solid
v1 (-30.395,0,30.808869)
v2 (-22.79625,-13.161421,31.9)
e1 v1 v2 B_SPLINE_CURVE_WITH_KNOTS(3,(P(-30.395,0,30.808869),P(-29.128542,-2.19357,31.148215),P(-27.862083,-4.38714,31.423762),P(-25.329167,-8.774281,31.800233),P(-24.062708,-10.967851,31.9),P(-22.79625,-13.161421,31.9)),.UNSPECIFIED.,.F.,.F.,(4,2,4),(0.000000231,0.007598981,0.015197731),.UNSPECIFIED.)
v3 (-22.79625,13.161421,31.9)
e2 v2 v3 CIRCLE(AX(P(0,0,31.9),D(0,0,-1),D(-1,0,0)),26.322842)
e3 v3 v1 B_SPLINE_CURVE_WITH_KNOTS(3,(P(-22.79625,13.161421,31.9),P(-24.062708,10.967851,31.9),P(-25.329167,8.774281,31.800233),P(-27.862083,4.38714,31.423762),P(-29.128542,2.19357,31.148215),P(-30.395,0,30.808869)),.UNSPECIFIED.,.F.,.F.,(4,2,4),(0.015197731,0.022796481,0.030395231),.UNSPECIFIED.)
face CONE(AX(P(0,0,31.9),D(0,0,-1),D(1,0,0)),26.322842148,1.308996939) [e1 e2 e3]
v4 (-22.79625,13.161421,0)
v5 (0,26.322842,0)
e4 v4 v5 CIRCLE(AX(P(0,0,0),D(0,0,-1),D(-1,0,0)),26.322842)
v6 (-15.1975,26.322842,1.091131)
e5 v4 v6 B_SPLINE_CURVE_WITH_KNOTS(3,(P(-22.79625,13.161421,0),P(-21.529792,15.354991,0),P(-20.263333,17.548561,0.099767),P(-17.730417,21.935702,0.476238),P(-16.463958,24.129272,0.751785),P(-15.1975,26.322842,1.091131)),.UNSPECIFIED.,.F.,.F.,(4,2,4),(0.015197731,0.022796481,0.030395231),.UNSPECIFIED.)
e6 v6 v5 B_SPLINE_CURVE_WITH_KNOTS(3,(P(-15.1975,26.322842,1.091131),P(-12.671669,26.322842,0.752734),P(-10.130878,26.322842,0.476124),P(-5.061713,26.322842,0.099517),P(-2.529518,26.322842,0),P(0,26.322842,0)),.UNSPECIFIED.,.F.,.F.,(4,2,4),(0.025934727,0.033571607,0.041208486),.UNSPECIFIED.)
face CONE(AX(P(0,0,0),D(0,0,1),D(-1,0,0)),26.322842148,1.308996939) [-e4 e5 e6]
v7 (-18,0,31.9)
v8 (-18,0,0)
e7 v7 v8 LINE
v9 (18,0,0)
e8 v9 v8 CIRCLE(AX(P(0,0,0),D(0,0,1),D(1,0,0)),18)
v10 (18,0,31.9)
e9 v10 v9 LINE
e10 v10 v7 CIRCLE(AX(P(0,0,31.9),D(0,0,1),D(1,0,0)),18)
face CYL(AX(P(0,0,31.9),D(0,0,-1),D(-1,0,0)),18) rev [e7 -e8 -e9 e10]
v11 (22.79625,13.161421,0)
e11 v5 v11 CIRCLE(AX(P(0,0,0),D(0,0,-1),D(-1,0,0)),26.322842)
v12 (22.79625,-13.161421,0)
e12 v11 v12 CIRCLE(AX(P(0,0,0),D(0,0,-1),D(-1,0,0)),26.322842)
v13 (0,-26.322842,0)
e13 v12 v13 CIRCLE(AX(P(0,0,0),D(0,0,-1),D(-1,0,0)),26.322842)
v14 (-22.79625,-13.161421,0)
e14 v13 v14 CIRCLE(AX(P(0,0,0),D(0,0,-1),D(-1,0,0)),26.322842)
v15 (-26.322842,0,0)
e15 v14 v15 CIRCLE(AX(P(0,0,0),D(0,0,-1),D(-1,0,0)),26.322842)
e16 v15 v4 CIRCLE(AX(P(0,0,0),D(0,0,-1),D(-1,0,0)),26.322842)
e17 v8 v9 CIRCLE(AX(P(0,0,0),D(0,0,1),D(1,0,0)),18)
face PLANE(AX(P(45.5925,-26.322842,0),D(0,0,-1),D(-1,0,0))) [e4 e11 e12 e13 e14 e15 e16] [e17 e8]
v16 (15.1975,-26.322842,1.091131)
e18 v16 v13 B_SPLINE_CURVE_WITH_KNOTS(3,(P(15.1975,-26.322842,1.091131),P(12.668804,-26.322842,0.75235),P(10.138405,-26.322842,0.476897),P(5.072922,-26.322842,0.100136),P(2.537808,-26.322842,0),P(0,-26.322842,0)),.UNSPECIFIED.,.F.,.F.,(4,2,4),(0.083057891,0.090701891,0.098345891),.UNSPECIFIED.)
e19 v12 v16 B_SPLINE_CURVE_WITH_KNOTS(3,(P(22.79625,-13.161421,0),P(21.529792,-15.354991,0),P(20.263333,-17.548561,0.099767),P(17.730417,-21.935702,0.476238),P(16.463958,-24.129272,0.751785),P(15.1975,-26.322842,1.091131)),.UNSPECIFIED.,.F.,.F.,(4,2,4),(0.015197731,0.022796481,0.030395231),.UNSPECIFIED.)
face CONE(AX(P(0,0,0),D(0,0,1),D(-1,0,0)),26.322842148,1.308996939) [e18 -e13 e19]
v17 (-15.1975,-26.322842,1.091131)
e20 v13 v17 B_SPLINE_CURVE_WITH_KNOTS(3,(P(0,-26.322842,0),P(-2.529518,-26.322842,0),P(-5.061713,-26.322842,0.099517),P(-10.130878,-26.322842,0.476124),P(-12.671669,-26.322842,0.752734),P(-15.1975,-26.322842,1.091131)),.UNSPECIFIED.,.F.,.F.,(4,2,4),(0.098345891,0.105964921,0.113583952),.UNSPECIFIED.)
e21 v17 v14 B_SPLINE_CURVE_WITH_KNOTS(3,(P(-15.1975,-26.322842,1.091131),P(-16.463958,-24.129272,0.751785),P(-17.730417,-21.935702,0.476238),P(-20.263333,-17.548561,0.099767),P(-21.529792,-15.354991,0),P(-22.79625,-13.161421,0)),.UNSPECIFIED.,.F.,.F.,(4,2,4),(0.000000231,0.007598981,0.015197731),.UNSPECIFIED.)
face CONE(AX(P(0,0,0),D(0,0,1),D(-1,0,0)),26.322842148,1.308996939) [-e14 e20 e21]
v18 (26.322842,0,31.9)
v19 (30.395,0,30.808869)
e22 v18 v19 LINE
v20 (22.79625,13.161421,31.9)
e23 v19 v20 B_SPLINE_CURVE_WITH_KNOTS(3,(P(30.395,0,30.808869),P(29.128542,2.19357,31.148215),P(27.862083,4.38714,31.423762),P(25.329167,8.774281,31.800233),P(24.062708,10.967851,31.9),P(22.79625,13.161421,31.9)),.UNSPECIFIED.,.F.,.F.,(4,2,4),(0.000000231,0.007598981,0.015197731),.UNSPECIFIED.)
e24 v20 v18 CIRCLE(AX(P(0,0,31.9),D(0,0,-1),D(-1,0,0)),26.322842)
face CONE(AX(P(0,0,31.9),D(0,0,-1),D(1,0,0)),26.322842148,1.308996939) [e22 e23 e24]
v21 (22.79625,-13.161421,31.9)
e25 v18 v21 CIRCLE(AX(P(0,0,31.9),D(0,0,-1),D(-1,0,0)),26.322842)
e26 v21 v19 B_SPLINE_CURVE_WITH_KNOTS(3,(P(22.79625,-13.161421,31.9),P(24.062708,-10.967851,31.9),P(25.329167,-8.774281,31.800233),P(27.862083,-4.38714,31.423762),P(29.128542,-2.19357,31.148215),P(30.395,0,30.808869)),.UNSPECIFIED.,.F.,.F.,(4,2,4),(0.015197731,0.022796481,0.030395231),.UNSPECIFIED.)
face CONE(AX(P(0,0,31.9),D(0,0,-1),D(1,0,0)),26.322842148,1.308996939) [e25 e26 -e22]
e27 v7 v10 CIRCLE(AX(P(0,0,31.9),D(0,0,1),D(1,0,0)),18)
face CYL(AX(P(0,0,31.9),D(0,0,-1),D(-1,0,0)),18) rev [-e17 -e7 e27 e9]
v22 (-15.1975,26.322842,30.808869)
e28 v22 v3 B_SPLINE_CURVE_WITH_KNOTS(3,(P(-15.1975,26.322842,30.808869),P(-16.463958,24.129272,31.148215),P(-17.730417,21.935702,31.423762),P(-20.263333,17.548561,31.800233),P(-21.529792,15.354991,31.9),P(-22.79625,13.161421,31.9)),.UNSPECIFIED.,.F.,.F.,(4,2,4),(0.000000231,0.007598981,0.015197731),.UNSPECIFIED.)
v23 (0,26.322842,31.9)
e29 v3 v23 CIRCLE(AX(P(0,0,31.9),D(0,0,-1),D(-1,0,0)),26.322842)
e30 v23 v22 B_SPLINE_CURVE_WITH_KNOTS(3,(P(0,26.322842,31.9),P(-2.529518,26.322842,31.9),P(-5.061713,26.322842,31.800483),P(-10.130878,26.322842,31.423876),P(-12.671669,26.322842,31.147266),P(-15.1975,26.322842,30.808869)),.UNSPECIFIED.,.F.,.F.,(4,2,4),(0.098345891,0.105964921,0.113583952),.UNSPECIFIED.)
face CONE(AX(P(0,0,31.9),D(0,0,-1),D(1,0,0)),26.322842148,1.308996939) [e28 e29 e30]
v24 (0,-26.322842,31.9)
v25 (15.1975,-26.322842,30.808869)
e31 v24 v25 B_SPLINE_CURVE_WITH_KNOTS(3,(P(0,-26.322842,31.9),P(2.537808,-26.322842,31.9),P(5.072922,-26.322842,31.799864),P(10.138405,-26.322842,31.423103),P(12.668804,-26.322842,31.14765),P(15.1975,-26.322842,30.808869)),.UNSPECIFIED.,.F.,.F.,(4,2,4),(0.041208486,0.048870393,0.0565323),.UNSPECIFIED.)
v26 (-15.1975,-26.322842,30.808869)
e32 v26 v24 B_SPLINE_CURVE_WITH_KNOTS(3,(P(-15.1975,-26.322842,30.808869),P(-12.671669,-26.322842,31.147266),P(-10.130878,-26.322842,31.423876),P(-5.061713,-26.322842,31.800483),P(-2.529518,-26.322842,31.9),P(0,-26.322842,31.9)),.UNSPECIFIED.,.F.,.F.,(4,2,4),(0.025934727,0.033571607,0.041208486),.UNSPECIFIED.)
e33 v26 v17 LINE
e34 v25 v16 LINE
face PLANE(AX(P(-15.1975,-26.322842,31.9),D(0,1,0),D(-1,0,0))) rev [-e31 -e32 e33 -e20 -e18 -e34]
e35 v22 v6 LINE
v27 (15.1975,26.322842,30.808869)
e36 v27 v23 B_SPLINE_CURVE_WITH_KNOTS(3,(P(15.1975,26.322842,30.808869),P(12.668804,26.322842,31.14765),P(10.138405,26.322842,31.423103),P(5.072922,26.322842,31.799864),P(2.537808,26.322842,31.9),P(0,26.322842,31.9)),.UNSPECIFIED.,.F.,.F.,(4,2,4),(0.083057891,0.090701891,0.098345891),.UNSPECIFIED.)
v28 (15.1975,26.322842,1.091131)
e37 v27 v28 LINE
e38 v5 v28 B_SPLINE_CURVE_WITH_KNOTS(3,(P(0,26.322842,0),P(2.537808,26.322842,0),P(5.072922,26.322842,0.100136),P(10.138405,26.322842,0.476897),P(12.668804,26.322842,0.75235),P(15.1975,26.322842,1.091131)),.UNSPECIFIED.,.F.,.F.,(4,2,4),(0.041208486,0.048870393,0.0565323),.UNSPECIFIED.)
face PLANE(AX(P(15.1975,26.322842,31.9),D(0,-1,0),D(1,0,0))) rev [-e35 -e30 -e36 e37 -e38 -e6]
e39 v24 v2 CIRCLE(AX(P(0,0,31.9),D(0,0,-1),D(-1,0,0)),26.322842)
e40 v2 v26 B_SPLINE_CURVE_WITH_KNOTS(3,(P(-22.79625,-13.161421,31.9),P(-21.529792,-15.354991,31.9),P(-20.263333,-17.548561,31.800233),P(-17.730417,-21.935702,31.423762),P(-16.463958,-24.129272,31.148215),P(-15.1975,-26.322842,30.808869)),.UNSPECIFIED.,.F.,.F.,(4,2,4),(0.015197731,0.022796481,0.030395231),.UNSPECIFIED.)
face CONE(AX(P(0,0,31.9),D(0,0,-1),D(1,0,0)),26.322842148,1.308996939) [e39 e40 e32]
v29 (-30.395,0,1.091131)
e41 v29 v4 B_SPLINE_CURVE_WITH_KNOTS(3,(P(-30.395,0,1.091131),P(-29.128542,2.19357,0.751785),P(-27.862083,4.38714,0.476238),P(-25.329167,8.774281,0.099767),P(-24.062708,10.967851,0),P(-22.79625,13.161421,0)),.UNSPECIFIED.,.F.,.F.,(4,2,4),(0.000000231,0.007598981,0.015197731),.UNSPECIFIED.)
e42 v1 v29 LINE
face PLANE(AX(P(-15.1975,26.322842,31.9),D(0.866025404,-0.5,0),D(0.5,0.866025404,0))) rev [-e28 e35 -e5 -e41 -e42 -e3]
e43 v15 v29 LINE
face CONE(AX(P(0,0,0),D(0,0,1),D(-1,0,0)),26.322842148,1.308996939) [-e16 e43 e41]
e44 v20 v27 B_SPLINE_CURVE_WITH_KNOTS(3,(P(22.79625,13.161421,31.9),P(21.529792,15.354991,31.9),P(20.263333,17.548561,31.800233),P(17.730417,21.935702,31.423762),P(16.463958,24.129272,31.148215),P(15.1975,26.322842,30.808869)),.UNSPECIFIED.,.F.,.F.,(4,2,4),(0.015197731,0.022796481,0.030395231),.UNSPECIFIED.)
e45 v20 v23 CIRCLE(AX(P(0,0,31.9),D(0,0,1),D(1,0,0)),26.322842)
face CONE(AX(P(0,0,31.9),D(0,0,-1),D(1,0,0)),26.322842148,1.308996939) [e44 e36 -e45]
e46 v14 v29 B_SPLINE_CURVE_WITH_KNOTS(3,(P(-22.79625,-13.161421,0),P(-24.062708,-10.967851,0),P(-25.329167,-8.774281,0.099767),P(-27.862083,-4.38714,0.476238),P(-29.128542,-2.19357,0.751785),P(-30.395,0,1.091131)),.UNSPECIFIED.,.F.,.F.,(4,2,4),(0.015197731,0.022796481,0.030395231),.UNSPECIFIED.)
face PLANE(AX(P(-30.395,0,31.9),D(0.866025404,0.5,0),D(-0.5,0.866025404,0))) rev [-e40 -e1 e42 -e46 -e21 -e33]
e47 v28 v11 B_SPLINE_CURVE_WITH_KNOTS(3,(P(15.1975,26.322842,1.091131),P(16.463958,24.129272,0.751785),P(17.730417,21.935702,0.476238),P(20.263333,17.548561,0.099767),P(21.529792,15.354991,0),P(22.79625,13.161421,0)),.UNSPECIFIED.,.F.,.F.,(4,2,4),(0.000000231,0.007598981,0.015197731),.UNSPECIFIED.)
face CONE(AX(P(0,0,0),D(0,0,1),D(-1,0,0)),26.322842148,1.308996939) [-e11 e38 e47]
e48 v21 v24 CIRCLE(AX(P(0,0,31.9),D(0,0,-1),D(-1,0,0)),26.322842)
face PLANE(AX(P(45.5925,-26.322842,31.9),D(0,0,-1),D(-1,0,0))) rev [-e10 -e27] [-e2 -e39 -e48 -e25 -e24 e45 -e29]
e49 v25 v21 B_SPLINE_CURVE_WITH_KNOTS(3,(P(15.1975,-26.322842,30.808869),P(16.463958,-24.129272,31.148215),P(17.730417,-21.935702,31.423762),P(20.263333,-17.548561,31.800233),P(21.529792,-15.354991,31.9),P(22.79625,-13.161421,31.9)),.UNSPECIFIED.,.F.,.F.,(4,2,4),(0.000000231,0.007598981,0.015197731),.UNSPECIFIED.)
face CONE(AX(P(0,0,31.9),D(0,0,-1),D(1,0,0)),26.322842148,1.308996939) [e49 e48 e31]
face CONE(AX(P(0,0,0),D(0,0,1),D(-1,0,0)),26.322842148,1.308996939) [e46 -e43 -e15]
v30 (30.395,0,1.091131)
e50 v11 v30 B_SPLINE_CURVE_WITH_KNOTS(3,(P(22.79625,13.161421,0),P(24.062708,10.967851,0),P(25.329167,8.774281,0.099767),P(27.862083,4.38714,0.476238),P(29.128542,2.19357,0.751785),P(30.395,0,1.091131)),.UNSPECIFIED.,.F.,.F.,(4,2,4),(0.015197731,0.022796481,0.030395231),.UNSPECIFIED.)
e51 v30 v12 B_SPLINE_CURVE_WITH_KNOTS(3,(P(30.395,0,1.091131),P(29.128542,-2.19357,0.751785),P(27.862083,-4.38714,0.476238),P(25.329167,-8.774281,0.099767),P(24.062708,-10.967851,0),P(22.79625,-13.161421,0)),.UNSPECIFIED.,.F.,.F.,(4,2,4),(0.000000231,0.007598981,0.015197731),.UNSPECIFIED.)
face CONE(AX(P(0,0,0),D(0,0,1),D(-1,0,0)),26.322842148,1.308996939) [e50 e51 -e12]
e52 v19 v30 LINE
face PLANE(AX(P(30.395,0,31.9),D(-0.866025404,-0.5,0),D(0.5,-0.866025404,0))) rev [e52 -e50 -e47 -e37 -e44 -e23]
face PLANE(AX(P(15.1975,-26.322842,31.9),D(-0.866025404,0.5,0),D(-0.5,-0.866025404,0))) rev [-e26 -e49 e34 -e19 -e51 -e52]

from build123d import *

# Parameters (mm, degrees)
SKETCH1_R          = 18
BASE_EXTRUDE_DEPTH = 31.9
SKETCH2_OUTSIDE_W  = 363.728
SKETCH2_OUTSIDE_H  = 355.584
SKETCH2_OUTSIDE_R  = 26.322842148
CUT_EXTRUDE1_DEPTH = 38
CUT_EXTRUDE1_DRAFT = -75
SKETCH3_OUTSIDE_W  = 363.728
SKETCH3_OUTSIDE_H  = 355.584
SKETCH3_OUTSIDE_R  = 26.322842148
CUT_EXTRUDE2_DEPTH = 38
CUT_EXTRUDE2_DRAFT = -75


with BuildPart() as part:
    # Sketch1 → Base-Extrude (new body)
    with BuildSketch(Plane.XY):
        Polygon((15.1975, 26.322842148), (-15.1975, 26.322842148), (-30.395, 0), (-15.1975, -26.322842148), (15.1975, -26.322842148), (30.395, 0), align=None)
        Circle(SKETCH1_R, mode=Mode.SUBTRACT)
    extrude(amount=BASE_EXTRUDE_DEPTH)


with BuildPart() as cut_extrude1_tool:
    # Sketch2 outside → Cut-Extrude1 (with draft: the straight prism first)
    with BuildSketch(Plane(origin=(0, 0, 0), x_dir=(-1, 0, 0), z_dir=(0, 0, -1))):
        Rectangle(SKETCH2_OUTSIDE_W, SKETCH2_OUTSIDE_H)
        Circle(SKETCH2_OUTSIDE_R, mode=Mode.SUBTRACT)
    extrude(amount=-CUT_EXTRUDE1_DEPTH)
    # Cut-Extrude1: the draft: its side faces are tilted about the plane it starts from
    cut_extrude1_sides = [cut_extrude1_tool.faces().sort_by_distance(p)[0] for p in [
        (0, -177.792, 19),
        (-181.864, 0, 19),
        (0, 177.792, 19),
        (181.864, 0, 19),
        (26.322842148, 0, 19),
    ]]
    draft(cut_extrude1_sides, Plane(origin=(0, 0, 0), x_dir=(-1, 0, 0), z_dir=(0, 0, -1)), CUT_EXTRUDE1_DRAFT)


with BuildPart() as part_1:
    add(part.part)

    # Cut-Extrude1: cut by cut_extrude1_tool
    add(cut_extrude1_tool.part, mode=Mode.SUBTRACT)


with BuildPart() as cut_extrude2_tool:
    # Sketch3 outside → Cut-Extrude2 (with draft: the straight prism first)
    with BuildSketch(Plane.XY.offset(31.9)):
        Rectangle(SKETCH3_OUTSIDE_W, SKETCH3_OUTSIDE_H)
        Circle(SKETCH3_OUTSIDE_R, mode=Mode.SUBTRACT)
    extrude(amount=-CUT_EXTRUDE2_DEPTH)
    # Cut-Extrude2: the draft: its side faces are tilted about the plane it starts from
    cut_extrude2_sides = [cut_extrude2_tool.faces().sort_by_distance(p)[0] for p in [
        (0, -177.792, 12.9),
        (181.864, 0, 12.9),
        (0, 177.792, 12.9),
        (-181.864, 0, 12.9),
        (-26.322842148, 0, 12.9),
    ]]
    draft(cut_extrude2_sides, Plane.XY.offset(31.9), CUT_EXTRUDE2_DRAFT)


with BuildPart() as part_2:
    add(part_1.part)

    # Cut-Extrude2: cut by cut_extrude2_tool
    add(cut_extrude2_tool.part, mode=Mode.SUBTRACT)


solid = part_2.part
